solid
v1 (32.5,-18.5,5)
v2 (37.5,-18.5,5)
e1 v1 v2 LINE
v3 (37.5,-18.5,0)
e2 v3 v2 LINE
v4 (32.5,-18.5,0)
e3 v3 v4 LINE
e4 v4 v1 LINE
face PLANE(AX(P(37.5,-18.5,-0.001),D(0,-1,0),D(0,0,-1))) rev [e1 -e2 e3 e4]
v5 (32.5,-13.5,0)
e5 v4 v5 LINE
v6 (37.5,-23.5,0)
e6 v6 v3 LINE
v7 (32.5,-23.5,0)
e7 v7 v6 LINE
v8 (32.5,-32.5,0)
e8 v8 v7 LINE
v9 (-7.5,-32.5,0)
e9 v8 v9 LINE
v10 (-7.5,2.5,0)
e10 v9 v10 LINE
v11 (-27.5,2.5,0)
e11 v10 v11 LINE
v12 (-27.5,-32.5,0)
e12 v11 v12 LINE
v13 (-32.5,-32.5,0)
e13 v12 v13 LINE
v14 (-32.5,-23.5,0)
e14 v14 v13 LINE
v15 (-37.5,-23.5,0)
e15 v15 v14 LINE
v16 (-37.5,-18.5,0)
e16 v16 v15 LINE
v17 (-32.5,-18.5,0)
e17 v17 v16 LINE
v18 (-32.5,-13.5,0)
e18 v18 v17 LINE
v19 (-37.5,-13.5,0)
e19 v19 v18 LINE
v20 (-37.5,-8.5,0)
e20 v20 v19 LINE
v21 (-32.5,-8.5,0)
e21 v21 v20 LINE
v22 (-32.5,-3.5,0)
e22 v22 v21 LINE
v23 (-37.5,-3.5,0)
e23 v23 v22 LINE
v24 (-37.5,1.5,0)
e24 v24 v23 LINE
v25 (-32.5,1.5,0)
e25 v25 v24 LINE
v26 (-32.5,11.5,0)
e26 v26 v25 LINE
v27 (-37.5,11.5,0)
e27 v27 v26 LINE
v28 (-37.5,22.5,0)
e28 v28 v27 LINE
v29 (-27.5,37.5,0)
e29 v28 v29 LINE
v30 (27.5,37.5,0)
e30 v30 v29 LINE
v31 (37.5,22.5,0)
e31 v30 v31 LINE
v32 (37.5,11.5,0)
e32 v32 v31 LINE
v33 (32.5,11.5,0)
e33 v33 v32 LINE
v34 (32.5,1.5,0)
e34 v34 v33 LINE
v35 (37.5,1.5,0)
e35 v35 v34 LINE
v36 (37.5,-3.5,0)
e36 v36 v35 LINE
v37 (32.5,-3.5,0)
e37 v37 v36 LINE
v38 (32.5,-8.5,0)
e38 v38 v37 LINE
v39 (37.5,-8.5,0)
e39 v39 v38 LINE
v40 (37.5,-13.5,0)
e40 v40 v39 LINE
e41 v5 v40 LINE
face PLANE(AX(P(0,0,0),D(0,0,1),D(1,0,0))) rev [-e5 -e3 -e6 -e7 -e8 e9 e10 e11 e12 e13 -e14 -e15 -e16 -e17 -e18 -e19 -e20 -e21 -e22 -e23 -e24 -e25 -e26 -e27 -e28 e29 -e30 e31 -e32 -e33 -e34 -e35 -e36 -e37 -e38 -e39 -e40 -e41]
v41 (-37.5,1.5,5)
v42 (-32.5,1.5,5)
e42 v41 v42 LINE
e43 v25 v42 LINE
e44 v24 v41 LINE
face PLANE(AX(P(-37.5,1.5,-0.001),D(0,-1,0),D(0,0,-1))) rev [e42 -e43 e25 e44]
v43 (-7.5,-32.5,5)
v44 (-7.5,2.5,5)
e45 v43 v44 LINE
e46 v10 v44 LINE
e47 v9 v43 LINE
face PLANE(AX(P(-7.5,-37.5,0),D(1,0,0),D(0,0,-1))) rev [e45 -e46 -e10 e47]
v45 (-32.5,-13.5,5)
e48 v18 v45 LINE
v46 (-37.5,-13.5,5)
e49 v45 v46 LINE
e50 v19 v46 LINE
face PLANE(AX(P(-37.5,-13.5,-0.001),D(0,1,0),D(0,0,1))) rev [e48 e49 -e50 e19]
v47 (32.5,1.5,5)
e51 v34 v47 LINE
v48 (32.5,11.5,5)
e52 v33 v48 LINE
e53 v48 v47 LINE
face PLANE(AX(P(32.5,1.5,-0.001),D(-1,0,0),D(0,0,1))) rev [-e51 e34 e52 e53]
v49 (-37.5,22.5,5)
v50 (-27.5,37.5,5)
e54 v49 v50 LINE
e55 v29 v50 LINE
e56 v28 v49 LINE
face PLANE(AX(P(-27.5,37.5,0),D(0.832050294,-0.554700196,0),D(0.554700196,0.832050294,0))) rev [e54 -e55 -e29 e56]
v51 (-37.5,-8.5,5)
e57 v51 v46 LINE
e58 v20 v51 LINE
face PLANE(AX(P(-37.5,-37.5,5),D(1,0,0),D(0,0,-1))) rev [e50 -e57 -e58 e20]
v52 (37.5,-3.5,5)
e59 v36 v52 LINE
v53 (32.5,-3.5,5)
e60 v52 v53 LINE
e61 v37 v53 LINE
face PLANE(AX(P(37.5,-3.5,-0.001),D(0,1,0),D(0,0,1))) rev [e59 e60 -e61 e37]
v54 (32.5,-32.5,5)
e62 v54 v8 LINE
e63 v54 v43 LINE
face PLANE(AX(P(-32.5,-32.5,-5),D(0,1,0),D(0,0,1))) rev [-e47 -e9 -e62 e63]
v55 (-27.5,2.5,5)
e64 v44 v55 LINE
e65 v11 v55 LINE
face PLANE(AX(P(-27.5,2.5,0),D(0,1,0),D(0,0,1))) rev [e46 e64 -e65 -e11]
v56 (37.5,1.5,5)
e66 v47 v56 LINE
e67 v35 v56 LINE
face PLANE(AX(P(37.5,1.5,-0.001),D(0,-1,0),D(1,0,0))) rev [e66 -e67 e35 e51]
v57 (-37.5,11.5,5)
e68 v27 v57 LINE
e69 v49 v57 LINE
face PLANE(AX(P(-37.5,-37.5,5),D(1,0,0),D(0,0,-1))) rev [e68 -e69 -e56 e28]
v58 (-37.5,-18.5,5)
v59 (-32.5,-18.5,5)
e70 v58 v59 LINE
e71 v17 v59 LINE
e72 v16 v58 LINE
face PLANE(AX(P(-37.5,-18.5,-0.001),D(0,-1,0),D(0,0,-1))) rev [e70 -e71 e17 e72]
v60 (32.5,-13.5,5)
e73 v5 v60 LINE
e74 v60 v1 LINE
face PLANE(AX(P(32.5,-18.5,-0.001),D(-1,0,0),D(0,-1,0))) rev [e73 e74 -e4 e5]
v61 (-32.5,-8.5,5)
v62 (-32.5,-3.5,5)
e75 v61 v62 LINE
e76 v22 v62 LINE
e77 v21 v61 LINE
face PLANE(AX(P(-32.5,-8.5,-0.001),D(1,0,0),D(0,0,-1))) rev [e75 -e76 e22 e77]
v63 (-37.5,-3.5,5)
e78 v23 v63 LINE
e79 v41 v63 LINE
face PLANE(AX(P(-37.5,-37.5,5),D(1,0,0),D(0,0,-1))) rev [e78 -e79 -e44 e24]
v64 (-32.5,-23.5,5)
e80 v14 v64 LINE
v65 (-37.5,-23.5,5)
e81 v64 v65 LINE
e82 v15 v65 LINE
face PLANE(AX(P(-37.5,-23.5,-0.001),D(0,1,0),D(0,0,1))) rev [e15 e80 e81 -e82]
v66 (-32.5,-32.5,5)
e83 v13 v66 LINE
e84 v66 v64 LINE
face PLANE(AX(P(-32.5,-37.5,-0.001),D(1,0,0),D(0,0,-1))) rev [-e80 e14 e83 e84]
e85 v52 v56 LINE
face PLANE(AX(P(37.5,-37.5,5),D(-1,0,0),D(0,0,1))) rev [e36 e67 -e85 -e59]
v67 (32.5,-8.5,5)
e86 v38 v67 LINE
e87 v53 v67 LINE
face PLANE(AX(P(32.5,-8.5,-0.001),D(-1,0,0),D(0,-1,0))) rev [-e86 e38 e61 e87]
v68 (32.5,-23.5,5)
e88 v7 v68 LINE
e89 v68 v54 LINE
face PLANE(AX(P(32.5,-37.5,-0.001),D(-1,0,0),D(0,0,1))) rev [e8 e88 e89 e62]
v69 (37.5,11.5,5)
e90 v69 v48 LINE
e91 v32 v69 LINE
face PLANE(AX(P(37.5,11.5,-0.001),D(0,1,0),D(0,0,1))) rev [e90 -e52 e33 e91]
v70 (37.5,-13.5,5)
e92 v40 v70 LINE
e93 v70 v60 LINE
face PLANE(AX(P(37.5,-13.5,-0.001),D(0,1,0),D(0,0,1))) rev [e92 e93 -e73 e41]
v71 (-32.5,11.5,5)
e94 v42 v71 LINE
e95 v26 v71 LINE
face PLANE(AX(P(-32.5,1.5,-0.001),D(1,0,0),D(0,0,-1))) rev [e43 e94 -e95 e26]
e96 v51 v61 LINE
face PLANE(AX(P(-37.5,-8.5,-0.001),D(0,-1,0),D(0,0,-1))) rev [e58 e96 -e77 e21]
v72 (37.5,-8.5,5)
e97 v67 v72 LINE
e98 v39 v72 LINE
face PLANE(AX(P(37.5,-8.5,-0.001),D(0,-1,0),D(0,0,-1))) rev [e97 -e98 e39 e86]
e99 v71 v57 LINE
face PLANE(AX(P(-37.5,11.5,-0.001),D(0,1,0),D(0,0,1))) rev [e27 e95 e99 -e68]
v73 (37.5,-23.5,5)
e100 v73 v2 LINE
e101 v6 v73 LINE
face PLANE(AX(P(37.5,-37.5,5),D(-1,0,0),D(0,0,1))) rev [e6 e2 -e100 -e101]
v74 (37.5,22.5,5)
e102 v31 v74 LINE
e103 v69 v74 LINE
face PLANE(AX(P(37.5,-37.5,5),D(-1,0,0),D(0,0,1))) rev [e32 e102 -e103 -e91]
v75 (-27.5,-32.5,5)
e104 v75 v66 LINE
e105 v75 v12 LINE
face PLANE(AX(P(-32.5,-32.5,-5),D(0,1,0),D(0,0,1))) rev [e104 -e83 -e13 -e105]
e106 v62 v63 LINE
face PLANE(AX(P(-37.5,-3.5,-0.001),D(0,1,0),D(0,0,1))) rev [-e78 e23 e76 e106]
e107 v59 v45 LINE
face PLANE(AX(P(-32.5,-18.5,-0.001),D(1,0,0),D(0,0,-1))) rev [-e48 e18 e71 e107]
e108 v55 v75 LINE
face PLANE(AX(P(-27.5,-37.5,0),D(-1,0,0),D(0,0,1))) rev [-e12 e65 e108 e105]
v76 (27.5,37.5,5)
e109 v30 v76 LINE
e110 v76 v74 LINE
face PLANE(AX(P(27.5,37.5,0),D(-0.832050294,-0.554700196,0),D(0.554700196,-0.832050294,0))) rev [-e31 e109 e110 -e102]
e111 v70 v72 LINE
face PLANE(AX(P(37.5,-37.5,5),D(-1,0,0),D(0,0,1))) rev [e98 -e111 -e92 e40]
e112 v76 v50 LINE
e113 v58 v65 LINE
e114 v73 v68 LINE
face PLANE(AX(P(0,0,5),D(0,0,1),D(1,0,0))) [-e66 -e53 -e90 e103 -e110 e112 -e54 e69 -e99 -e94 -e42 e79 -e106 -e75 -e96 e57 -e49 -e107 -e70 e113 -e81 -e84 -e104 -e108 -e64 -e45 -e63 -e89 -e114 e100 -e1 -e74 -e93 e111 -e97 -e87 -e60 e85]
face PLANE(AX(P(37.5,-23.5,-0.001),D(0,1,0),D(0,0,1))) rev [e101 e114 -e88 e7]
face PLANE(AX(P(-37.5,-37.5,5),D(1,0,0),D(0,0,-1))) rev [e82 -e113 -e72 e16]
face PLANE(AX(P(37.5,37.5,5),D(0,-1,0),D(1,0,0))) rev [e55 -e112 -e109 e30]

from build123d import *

# Parameters (mm, degrees)
SKETCH1_W           = 75
SKETCH1_H           = 75
BOSS_EXTRUDE1_DEPTH = 5
CUT_EXTRUDE1_DEPTH  = 5
SKETCH3_W           = 20
SKETCH3_H           = 40
CUT_EXTRUDE2_DEPTH  = 5
CUT_EXTRUDE3_REACH  = 55.268
SKETCH4_W           = 5
SKETCH4_H           = 14
SKETCH4_H_2         = 5
SKETCH4_H_3         = 10
CUT_EXTRUDE4_REACH  = 55.268
SKETCH5_W           = 5
SKETCH5_H           = 5
SKETCH5_H_2         = 14
SKETCH5_H_3         = 10
SKETCH7_W           = 65
SKETCH7_H           = 5
CUT_EXTRUDE5_DEPTH  = 10


with BuildPart() as part:
    # Sketch1 → Boss-Extrude1 (new body)
    with BuildSketch(Plane.XY):
        Rectangle(SKETCH1_W, SKETCH1_H)
    extrude(amount=BOSS_EXTRUDE1_DEPTH)

    # Sketch2 → Cut-Extrude1 (cut)
    with BuildSketch(Plane.XY.offset(5)):
        Polygon((-27.5, 37.5), (-37.5, 22.5), (-37.5, 37.5), align=None)
        Polygon((37.5, 37.5), (27.5, 37.5), (37.5, 22.5), align=None)
    extrude(amount=-CUT_EXTRUDE1_DEPTH, mode=Mode.SUBTRACT)

    # Sketch3 → Cut-Extrude2 (cut)
    with BuildSketch(Plane.XY.offset(5)):
        with Locations((-17.5, -17.5)):
            Rectangle(SKETCH3_W, SKETCH3_H)
    extrude(amount=-CUT_EXTRUDE2_DEPTH, mode=Mode.SUBTRACT)

    # Sketch4 → Cut-Extrude3 (cut, up to next)
    with BuildSketch(Plane.XY.offset(5), mode=Mode.PRIVATE) as cut_extrude3_sk1:
        with Locations((-35, -30.5)):
            Rectangle(SKETCH4_W, SKETCH4_H)
    cut_extrude3_tool1 = extrude(cut_extrude3_sk1.sketch, amount=-CUT_EXTRUDE3_REACH, mode=Mode.PRIVATE) & part.part
    # Sketch4 → Cut-Extrude3 (cut, up to next)
    with BuildSketch(Plane.XY.offset(5), mode=Mode.PRIVATE) as cut_extrude3_sk2:
        with Locations((-35, -16)):
            Rectangle(SKETCH4_W, SKETCH4_H_2)
    cut_extrude3_tool2 = extrude(cut_extrude3_sk2.sketch, amount=-CUT_EXTRUDE3_REACH, mode=Mode.PRIVATE) & part.part
    # Sketch4 → Cut-Extrude3 (cut, up to next)
    with BuildSketch(Plane.XY.offset(5), mode=Mode.PRIVATE) as cut_extrude3_sk3:
        with Locations((-35, -6)):
            Rectangle(SKETCH4_W, SKETCH4_H_2)
    cut_extrude3_tool3 = extrude(cut_extrude3_sk3.sketch, amount=-CUT_EXTRUDE3_REACH, mode=Mode.PRIVATE) & part.part
    # Sketch4 → Cut-Extrude3 (cut, up to next)
    with BuildSketch(Plane.XY.offset(5), mode=Mode.PRIVATE) as cut_extrude3_sk4:
        with Locations((-35, 6.5)):
            Rectangle(SKETCH4_W, SKETCH4_H_3)
    cut_extrude3_tool4 = extrude(cut_extrude3_sk4.sketch, amount=-CUT_EXTRUDE3_REACH, mode=Mode.PRIVATE) & part.part
    add(cut_extrude3_tool1.solids().sort_by_distance((-35, -30.5, 5))[0], mode=Mode.SUBTRACT)
    add(cut_extrude3_tool2.solids().sort_by_distance((-35, -16, 5))[0], mode=Mode.SUBTRACT)
    add(cut_extrude3_tool3.solids().sort_by_distance((-35, -6, 5))[0], mode=Mode.SUBTRACT)
    add(cut_extrude3_tool4.solids().sort_by_distance((-35, 6.5, 5))[0], mode=Mode.SUBTRACT)

    # Sketch5 → Cut-Extrude4 (cut, up to next)
    with BuildSketch(Plane.XY.offset(5), mode=Mode.PRIVATE) as cut_extrude4_sk1:
        with Locations((35, -16)):
            Rectangle(SKETCH5_W, SKETCH5_H)
    cut_extrude4_tool1 = extrude(cut_extrude4_sk1.sketch, amount=-CUT_EXTRUDE4_REACH, mode=Mode.PRIVATE) & part.part
    # Sketch5 → Cut-Extrude4 (cut, up to next)
    with BuildSketch(Plane.XY.offset(5), mode=Mode.PRIVATE) as cut_extrude4_sk2:
        with Locations((35, -6)):
            Rectangle(SKETCH5_W, SKETCH5_H)
    cut_extrude4_tool2 = extrude(cut_extrude4_sk2.sketch, amount=-CUT_EXTRUDE4_REACH, mode=Mode.PRIVATE) & part.part
    # Sketch5 → Cut-Extrude4 (cut, up to next)
    with BuildSketch(Plane.XY.offset(5), mode=Mode.PRIVATE) as cut_extrude4_sk3:
        with Locations((35, -30.5)):
            Rectangle(SKETCH5_W, SKETCH5_H_2)
    cut_extrude4_tool3 = extrude(cut_extrude4_sk3.sketch, amount=-CUT_EXTRUDE4_REACH, mode=Mode.PRIVATE) & part.part
    # Sketch5 → Cut-Extrude4 (cut, up to next)
    with BuildSketch(Plane.XY.offset(5), mode=Mode.PRIVATE) as cut_extrude4_sk4:
        with Locations((35, 6.5)):
            Rectangle(SKETCH5_W, SKETCH5_H_3)
    cut_extrude4_tool4 = extrude(cut_extrude4_sk4.sketch, amount=-CUT_EXTRUDE4_REACH, mode=Mode.PRIVATE) & part.part
    add(cut_extrude4_tool1.solids().sort_by_distance((35, -16, 5))[0], mode=Mode.SUBTRACT)
    add(cut_extrude4_tool2.solids().sort_by_distance((35, -6, 5))[0], mode=Mode.SUBTRACT)
    add(cut_extrude4_tool3.solids().sort_by_distance((35, -30.5, 5))[0], mode=Mode.SUBTRACT)
    add(cut_extrude4_tool4.solids().sort_by_distance((35, 6.5, 5))[0], mode=Mode.SUBTRACT)

    # Sketch7 → Cut-Extrude5 (cut)
    with BuildSketch(Plane.XY.offset(5)):
        with Locations((0, -35)):
            Rectangle(SKETCH7_W, SKETCH7_H)
    extrude(amount=-CUT_EXTRUDE5_DEPTH, mode=Mode.SUBTRACT)


solid = part.part
